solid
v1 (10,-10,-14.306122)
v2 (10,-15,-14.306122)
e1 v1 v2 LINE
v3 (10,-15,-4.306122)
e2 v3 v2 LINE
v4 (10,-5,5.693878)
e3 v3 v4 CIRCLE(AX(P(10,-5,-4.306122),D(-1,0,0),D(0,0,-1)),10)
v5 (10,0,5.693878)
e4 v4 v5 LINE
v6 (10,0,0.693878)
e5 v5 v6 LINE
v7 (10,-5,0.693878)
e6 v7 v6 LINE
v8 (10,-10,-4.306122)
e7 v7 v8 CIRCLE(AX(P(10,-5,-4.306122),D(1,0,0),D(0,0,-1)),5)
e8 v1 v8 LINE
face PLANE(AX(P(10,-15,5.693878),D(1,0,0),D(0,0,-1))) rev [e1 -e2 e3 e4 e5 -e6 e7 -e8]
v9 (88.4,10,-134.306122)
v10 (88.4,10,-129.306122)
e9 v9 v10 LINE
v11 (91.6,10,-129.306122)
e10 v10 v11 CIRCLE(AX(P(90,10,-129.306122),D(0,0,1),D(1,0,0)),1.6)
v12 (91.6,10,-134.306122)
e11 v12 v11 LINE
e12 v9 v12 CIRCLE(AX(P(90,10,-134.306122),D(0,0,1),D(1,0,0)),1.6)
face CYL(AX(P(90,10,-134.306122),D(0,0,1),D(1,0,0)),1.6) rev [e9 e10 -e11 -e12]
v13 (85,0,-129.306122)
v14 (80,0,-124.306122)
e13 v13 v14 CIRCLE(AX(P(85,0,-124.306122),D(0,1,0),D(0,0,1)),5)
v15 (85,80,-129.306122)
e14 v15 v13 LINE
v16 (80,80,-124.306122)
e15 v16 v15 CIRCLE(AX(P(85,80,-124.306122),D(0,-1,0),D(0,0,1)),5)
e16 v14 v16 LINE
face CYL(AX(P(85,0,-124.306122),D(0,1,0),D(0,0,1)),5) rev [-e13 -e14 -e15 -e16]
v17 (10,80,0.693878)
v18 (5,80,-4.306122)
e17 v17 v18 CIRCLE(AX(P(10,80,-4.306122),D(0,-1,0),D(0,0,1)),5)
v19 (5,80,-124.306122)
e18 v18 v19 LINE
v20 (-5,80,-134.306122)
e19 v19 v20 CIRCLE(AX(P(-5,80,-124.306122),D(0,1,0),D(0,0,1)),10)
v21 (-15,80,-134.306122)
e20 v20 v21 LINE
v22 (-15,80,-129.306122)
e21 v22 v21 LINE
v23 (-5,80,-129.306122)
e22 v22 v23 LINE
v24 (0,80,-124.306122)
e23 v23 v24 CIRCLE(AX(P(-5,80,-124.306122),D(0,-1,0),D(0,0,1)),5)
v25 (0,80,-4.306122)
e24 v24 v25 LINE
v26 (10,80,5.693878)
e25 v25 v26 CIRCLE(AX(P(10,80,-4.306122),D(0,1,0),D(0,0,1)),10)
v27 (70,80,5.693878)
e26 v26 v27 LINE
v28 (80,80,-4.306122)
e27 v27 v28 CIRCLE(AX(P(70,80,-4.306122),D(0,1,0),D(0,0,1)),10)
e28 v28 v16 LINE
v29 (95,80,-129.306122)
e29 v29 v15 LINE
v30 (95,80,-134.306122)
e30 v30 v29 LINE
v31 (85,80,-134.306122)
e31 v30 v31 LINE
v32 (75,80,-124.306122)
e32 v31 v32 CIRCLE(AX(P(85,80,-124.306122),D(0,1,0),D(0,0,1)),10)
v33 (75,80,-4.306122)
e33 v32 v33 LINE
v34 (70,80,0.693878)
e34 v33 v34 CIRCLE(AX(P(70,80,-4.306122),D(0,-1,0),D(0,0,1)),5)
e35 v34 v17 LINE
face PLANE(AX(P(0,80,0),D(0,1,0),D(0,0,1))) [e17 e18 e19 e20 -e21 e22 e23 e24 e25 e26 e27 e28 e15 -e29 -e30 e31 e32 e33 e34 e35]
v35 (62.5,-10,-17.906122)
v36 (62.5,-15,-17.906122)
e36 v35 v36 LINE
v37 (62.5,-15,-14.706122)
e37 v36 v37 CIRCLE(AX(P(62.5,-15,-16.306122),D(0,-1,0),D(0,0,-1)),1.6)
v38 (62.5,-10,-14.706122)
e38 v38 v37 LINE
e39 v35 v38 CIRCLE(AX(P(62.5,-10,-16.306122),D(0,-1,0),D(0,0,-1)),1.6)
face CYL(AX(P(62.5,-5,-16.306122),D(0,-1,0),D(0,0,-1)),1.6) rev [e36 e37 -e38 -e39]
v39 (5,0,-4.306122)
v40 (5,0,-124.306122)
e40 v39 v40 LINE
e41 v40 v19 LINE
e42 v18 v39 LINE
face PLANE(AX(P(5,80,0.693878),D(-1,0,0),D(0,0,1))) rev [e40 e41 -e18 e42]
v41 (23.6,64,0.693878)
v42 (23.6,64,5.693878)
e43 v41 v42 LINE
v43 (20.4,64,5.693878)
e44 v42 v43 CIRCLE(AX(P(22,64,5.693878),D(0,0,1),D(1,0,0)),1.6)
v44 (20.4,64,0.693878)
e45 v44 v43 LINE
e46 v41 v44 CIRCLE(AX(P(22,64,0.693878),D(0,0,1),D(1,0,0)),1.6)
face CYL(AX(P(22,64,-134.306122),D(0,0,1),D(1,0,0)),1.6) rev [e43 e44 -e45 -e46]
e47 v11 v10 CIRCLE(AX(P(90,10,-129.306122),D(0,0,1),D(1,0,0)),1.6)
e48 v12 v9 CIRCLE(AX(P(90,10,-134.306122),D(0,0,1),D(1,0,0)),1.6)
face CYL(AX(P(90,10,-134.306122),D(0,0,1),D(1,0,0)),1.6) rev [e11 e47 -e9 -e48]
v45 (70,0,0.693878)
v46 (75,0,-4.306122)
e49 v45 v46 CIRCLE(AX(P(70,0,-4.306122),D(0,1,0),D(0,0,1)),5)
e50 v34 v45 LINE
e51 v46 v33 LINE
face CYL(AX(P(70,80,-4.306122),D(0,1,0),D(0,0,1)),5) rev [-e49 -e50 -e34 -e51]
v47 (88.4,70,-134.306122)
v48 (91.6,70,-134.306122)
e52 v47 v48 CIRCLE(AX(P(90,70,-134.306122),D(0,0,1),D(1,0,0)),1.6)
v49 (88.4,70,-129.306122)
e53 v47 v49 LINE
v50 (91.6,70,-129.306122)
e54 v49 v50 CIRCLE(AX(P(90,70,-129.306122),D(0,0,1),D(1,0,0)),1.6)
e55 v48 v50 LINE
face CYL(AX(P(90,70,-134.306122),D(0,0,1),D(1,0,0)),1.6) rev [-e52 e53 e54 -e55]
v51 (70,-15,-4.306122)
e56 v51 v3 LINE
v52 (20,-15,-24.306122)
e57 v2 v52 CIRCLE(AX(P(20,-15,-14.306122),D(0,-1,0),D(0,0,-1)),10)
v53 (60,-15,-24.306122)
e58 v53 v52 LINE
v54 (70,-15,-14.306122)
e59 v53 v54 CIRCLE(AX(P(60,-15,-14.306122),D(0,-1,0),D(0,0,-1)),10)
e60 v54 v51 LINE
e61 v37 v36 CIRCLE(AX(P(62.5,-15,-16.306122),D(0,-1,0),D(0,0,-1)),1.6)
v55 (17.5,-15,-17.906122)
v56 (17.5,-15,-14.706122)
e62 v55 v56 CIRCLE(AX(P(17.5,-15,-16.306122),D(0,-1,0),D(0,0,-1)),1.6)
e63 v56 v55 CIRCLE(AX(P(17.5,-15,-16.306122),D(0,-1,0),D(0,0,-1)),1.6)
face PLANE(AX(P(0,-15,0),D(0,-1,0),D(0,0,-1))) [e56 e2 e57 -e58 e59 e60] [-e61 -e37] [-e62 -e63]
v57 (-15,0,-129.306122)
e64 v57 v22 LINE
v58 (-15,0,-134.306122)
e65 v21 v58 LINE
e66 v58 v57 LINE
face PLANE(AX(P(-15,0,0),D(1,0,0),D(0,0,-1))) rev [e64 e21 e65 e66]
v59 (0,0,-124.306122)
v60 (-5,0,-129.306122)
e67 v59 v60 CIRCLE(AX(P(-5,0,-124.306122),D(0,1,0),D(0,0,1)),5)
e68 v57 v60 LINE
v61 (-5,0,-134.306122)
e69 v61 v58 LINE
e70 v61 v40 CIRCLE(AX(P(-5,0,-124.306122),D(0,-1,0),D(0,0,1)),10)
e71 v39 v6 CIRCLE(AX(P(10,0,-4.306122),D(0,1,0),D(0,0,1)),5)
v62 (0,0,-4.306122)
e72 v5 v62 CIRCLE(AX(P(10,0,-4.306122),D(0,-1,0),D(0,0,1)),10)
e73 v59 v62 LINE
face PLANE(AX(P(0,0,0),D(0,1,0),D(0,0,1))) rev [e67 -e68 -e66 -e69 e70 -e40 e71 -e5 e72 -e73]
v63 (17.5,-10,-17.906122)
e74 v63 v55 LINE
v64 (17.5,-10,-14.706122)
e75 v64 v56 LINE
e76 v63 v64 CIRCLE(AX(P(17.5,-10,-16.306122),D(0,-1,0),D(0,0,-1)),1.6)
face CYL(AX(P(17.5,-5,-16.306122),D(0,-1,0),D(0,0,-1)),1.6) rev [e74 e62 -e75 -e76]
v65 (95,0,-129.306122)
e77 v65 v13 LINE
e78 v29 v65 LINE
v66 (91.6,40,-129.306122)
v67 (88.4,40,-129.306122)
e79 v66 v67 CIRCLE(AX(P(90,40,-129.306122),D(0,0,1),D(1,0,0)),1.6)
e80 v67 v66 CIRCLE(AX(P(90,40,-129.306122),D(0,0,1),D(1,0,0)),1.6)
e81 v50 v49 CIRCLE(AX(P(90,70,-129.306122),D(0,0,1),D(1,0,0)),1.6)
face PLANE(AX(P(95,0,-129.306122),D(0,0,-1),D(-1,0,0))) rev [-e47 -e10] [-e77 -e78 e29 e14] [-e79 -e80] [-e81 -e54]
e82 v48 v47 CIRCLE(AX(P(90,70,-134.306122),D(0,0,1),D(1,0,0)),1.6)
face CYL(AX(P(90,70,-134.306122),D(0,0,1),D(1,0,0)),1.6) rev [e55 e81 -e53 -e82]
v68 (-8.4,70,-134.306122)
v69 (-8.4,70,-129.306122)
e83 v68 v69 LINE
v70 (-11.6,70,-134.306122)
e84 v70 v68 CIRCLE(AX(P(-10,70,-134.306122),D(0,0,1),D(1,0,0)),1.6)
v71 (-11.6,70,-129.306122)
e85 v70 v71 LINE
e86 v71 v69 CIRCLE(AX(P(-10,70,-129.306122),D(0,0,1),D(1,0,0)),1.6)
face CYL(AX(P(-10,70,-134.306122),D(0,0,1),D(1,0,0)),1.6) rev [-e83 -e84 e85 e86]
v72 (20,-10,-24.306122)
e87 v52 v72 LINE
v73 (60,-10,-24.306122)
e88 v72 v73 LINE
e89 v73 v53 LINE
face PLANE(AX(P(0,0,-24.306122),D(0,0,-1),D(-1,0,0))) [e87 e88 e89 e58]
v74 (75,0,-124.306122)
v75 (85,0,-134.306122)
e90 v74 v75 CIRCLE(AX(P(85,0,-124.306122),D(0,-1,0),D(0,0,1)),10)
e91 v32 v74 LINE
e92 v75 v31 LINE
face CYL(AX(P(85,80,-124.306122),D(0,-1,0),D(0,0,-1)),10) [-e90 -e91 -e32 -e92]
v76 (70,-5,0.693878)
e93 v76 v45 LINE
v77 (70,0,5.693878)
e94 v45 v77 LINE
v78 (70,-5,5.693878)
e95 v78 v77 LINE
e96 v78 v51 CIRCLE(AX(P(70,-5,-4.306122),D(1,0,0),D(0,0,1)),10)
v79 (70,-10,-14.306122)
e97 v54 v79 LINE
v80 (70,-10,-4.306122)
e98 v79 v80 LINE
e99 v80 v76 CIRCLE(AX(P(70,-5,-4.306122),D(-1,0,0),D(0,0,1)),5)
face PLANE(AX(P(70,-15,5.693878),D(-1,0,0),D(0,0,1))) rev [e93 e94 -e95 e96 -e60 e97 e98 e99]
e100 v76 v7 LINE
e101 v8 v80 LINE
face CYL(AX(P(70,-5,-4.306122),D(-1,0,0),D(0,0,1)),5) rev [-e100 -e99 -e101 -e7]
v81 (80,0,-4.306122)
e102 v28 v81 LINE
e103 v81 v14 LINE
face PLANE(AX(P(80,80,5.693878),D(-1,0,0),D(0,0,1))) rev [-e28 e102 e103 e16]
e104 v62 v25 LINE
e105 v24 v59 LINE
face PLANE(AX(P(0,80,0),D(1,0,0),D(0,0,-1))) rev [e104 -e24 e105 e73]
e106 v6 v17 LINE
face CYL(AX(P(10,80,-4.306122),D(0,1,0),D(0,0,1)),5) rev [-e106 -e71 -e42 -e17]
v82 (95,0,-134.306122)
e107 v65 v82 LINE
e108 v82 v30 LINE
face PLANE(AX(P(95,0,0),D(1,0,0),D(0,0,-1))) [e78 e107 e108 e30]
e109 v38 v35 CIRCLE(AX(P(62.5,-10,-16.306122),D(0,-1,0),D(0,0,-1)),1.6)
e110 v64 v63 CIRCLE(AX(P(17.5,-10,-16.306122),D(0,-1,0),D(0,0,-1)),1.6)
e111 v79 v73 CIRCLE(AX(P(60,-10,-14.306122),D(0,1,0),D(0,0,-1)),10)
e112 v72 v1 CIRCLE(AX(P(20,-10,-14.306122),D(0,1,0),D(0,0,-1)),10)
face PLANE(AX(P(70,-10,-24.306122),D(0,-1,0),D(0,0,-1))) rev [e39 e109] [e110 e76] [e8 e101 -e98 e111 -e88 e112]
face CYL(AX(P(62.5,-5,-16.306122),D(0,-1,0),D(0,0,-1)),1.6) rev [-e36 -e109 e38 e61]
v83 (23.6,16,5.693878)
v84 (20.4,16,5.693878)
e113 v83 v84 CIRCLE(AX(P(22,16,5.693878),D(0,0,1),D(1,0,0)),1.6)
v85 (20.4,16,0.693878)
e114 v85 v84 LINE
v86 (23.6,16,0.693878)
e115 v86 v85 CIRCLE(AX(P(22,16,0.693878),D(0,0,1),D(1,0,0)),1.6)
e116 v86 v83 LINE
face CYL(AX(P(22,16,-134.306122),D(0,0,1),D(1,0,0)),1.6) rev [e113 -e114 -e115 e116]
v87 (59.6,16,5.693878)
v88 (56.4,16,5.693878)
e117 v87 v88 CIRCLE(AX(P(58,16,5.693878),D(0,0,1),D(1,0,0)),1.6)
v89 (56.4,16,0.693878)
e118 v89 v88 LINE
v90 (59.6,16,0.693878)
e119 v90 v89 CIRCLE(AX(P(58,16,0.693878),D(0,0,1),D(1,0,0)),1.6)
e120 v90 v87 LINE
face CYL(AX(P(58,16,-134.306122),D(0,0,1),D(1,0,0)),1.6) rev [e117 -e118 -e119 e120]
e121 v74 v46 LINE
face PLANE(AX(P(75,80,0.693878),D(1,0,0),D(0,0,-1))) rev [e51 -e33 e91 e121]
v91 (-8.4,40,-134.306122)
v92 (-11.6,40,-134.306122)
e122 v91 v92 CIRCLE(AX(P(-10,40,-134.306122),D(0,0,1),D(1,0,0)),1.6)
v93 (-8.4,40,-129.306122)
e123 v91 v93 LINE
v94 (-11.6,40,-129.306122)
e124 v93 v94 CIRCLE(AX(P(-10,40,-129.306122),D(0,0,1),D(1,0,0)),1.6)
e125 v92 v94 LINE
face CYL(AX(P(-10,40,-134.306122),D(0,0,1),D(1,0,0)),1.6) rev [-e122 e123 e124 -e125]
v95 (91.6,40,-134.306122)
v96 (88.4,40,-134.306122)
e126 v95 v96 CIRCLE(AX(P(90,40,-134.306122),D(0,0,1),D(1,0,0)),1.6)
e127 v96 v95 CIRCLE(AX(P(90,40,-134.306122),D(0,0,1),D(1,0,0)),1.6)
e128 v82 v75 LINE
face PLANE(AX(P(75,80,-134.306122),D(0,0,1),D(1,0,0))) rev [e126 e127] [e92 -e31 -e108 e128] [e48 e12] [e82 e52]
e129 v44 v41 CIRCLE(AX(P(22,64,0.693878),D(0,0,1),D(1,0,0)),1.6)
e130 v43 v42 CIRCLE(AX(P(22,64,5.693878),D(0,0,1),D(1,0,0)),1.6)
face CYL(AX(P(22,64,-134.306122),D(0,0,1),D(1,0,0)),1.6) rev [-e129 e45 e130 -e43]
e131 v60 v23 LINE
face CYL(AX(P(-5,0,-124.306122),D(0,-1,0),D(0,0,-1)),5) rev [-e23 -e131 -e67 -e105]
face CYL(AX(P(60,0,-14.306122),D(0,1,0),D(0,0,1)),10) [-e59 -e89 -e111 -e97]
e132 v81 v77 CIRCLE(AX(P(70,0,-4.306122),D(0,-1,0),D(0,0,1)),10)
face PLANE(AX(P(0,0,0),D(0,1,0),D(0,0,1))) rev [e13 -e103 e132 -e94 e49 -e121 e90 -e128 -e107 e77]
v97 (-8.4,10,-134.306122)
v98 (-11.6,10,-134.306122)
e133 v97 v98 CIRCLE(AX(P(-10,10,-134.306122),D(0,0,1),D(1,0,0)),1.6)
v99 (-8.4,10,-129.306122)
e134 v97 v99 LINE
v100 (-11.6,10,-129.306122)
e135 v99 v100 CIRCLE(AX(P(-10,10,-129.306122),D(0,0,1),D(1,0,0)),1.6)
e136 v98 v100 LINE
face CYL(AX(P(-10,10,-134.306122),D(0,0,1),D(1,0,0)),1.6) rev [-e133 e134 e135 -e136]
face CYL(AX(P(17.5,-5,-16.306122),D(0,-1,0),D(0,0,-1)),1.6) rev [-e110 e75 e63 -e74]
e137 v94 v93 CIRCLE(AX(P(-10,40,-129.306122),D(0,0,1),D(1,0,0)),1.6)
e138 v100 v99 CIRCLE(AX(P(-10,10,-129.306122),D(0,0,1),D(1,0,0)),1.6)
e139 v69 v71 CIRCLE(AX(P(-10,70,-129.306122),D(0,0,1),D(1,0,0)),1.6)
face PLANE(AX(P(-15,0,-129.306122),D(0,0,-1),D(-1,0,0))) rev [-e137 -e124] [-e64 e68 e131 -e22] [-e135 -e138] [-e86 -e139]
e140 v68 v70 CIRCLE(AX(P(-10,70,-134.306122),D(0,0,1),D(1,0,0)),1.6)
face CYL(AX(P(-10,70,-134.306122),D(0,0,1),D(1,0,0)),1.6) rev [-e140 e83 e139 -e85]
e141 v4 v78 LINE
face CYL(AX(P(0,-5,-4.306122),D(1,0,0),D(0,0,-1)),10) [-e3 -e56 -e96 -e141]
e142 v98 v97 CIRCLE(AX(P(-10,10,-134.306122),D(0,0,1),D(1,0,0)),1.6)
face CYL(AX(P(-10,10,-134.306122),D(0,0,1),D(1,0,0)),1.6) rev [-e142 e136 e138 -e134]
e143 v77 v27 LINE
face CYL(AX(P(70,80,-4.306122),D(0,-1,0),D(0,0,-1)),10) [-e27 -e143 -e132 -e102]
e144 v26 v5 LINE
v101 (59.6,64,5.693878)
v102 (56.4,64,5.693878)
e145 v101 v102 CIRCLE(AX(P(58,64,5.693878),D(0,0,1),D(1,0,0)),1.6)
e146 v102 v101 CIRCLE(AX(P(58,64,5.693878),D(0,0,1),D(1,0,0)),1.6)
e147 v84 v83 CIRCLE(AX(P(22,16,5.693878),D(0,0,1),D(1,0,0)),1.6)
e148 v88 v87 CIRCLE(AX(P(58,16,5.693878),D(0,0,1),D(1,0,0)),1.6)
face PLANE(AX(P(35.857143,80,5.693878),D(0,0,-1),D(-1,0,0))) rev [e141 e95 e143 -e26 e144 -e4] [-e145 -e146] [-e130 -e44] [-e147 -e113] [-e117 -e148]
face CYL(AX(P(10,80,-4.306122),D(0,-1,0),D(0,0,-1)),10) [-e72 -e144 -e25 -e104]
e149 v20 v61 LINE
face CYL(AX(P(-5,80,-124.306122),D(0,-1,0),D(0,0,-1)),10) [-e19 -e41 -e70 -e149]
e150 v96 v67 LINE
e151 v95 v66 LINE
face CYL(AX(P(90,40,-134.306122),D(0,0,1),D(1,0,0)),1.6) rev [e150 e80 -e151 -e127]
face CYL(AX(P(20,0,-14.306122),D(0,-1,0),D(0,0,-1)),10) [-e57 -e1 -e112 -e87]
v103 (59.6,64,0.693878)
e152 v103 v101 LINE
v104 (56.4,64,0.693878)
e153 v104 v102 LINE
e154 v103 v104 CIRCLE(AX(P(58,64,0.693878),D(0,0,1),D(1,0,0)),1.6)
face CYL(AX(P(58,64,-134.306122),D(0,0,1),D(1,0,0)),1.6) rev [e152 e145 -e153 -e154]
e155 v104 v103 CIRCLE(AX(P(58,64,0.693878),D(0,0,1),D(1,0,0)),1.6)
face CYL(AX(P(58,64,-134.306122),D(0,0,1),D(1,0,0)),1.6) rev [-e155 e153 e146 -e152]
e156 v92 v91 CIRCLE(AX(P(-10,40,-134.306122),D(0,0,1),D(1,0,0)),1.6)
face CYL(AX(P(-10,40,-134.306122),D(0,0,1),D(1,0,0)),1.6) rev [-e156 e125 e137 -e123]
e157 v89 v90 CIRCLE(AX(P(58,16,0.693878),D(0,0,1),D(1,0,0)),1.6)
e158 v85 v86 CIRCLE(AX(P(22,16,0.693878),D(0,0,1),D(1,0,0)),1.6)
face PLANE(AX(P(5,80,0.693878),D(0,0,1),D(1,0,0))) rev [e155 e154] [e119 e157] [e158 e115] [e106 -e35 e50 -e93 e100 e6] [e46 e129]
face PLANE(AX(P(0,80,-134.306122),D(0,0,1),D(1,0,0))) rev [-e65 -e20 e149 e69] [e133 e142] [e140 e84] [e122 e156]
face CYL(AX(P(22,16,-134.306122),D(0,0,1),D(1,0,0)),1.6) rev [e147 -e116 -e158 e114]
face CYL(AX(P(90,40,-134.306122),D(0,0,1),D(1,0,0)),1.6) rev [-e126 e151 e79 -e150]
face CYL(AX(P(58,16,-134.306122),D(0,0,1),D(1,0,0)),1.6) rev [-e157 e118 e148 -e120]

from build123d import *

# Parameters (mm, degrees)
BOSS_EXTRUDE1_DEPTH = 80
SKETCH2_W           = 5
SKETCH2_H           = 80
BOSS_EXTRUDE2_DEPTH = 15
SKETCH3_W           = 5
SKETCH3_H           = 80
BOSS_EXTRUDE3_DEPTH = 15
FILLET1_R           = 10
FILLET2_R           = 5
SKETCH4_W           = 60
SKETCH4_H           = 5
BOSS_EXTRUDE4_DEPTH = 15
SKETCH5_W           = 60
SKETCH5_H           = 5
BOSS_EXTRUDE5_DEPTH = 25
FILLET3_R           = 5
FILLET4_R           = 10
SKETCH6_R           = 1.6
CUT_EXTRUDE1_DEPTH  = 10
FILLET5_R           = 10
SKETCH7_R           = 1.6
CUT_EXTRUDE2_DEPTH  = 188.149672722
SKETCH8_R           = 1.6
CUT_EXTRUDE3_DEPTH  = 184.439363278


with BuildPart() as part:
    # Sketch1 → Boss-Extrude1 (new body)
    with BuildSketch(Plane(origin=(0, 0, 0), x_dir=(1, 0, 0), z_dir=(0, 1, 0))):
        Polygon((0, 0), (0, 134.306122449), (5, 134.306122449), (5, -0.693877551), (75, -0.693877551), (75, 134.306122449), (80, 134.306122449), (80, -5.693877551), (35.857142857, -5.693877551), (0, -5.693877551), align=None)
    extrude(amount=BOSS_EXTRUDE1_DEPTH)

    # Sketch2 → Boss-Extrude2 (add)
    with BuildSketch(Plane(origin=(80, 0, 0), x_dir=(0, 0, -1), z_dir=(1, 0, 0))):
        with Locations((131.806122449, 40)):
            Rectangle(SKETCH2_W, SKETCH2_H)
    extrude(amount=BOSS_EXTRUDE2_DEPTH)

    # Sketch3 → Boss-Extrude3 (add)
    with BuildSketch(Plane.ZY):
        with Locations((-131.806122449, 40)):
            Rectangle(SKETCH3_W, SKETCH3_H)
    extrude(amount=BOSS_EXTRUDE3_DEPTH)

    # Fillet1
    fillet1_edges = [part.edges().sort_by_distance(p)[0] for p in [
        (5, 40, -134.306122449),
        (75, 40, -134.306122449),
        (80, 40, 5.693877551),
        (0, 40, 5.693877551),
    ]]
    fillet(fillet1_edges, radius=FILLET1_R)

    # Fillet2
    fillet2_edges = [part.edges().sort_by_distance(p)[0] for p in [
        (5, 40, 0.693877551),
        (75, 40, 0.693877551),
        (80, 40, -129.306122449),
        (0, 40, -129.306122449),
    ]]
    fillet(fillet2_edges, radius=FILLET2_R)

    # Sketch4 → Boss-Extrude4 (add)
    with BuildSketch(Plane.XZ):
        with Locations((40, 3.193877551)):
            Rectangle(SKETCH4_W, SKETCH4_H)
    extrude(amount=BOSS_EXTRUDE4_DEPTH)

    # Sketch5 → Boss-Extrude5 (add)
    with BuildSketch(Plane(origin=(0, 0, 0.693877551), x_dir=(-1, 0, 0), z_dir=(0, 0, -1))):
        with Locations((-40, -12.5)):
            Rectangle(SKETCH5_W, SKETCH5_H)
    extrude(amount=BOSS_EXTRUDE5_DEPTH)

    # Fillet3
    fillet3_edges = [part.edges().sort_by_distance(p)[0] for p in [
        (40, -10, 0.693877551),
    ]]
    fillet(fillet3_edges, radius=FILLET3_R)

    # Fillet4
    fillet4_edges = [part.edges().sort_by_distance(p)[0] for p in [
        (40, -15, 5.693877551),
    ]]
    fillet(fillet4_edges, radius=FILLET4_R)

    # Sketch6 → Cut-Extrude1 (cut)
    with BuildSketch(Plane.XZ.offset(15)):
        with Locations(Location((17.5, -16.306122449, 0), (0, 0, 270))):
            Circle(SKETCH6_R)
        with Locations(Location((62.5, -16.306122449, 0), (0, 0, 270))):
            Circle(SKETCH6_R)
    extrude(amount=-CUT_EXTRUDE1_DEPTH, mode=Mode.SUBTRACT)

    # Fillet5
    fillet5_edges = [part.edges().sort_by_distance(p)[0] for p in [
        (70, -12.5, -24.306122449),
        (10, -12.5, -24.306122449),
    ]]
    fillet(fillet5_edges, radius=FILLET5_R)

    # Sketch7 → Cut-Extrude2 (cut, through all)
    with BuildSketch(Plane.XY.offset(5.693877551)):
        with Locations((22, 64)):
            Circle(SKETCH7_R)
        with Locations((58, 64)):
            Circle(SKETCH7_R)
        with Locations((58, 16)):
            Circle(SKETCH7_R)
        with Locations((22, 16)):
            Circle(SKETCH7_R)
    extrude(amount=-CUT_EXTRUDE2_DEPTH, mode=Mode.SUBTRACT)

    # Sketch8 → Cut-Extrude3 (cut, through all)
    with BuildSketch(Plane.XY.offset(-129.306122449)):
        with Locations((-10, 70)):
            Circle(SKETCH8_R)
        with Locations((-10, 40)):
            Circle(SKETCH8_R)
        with Locations((-10, 10)):
            Circle(SKETCH8_R)
        with Locations((90, 70)):
            Circle(SKETCH8_R)
        with Locations((90, 40)):
            Circle(SKETCH8_R)
        with Locations((90, 10)):
            Circle(SKETCH8_R)
    extrude(amount=-CUT_EXTRUDE3_DEPTH, mode=Mode.SUBTRACT)


solid = part.part
